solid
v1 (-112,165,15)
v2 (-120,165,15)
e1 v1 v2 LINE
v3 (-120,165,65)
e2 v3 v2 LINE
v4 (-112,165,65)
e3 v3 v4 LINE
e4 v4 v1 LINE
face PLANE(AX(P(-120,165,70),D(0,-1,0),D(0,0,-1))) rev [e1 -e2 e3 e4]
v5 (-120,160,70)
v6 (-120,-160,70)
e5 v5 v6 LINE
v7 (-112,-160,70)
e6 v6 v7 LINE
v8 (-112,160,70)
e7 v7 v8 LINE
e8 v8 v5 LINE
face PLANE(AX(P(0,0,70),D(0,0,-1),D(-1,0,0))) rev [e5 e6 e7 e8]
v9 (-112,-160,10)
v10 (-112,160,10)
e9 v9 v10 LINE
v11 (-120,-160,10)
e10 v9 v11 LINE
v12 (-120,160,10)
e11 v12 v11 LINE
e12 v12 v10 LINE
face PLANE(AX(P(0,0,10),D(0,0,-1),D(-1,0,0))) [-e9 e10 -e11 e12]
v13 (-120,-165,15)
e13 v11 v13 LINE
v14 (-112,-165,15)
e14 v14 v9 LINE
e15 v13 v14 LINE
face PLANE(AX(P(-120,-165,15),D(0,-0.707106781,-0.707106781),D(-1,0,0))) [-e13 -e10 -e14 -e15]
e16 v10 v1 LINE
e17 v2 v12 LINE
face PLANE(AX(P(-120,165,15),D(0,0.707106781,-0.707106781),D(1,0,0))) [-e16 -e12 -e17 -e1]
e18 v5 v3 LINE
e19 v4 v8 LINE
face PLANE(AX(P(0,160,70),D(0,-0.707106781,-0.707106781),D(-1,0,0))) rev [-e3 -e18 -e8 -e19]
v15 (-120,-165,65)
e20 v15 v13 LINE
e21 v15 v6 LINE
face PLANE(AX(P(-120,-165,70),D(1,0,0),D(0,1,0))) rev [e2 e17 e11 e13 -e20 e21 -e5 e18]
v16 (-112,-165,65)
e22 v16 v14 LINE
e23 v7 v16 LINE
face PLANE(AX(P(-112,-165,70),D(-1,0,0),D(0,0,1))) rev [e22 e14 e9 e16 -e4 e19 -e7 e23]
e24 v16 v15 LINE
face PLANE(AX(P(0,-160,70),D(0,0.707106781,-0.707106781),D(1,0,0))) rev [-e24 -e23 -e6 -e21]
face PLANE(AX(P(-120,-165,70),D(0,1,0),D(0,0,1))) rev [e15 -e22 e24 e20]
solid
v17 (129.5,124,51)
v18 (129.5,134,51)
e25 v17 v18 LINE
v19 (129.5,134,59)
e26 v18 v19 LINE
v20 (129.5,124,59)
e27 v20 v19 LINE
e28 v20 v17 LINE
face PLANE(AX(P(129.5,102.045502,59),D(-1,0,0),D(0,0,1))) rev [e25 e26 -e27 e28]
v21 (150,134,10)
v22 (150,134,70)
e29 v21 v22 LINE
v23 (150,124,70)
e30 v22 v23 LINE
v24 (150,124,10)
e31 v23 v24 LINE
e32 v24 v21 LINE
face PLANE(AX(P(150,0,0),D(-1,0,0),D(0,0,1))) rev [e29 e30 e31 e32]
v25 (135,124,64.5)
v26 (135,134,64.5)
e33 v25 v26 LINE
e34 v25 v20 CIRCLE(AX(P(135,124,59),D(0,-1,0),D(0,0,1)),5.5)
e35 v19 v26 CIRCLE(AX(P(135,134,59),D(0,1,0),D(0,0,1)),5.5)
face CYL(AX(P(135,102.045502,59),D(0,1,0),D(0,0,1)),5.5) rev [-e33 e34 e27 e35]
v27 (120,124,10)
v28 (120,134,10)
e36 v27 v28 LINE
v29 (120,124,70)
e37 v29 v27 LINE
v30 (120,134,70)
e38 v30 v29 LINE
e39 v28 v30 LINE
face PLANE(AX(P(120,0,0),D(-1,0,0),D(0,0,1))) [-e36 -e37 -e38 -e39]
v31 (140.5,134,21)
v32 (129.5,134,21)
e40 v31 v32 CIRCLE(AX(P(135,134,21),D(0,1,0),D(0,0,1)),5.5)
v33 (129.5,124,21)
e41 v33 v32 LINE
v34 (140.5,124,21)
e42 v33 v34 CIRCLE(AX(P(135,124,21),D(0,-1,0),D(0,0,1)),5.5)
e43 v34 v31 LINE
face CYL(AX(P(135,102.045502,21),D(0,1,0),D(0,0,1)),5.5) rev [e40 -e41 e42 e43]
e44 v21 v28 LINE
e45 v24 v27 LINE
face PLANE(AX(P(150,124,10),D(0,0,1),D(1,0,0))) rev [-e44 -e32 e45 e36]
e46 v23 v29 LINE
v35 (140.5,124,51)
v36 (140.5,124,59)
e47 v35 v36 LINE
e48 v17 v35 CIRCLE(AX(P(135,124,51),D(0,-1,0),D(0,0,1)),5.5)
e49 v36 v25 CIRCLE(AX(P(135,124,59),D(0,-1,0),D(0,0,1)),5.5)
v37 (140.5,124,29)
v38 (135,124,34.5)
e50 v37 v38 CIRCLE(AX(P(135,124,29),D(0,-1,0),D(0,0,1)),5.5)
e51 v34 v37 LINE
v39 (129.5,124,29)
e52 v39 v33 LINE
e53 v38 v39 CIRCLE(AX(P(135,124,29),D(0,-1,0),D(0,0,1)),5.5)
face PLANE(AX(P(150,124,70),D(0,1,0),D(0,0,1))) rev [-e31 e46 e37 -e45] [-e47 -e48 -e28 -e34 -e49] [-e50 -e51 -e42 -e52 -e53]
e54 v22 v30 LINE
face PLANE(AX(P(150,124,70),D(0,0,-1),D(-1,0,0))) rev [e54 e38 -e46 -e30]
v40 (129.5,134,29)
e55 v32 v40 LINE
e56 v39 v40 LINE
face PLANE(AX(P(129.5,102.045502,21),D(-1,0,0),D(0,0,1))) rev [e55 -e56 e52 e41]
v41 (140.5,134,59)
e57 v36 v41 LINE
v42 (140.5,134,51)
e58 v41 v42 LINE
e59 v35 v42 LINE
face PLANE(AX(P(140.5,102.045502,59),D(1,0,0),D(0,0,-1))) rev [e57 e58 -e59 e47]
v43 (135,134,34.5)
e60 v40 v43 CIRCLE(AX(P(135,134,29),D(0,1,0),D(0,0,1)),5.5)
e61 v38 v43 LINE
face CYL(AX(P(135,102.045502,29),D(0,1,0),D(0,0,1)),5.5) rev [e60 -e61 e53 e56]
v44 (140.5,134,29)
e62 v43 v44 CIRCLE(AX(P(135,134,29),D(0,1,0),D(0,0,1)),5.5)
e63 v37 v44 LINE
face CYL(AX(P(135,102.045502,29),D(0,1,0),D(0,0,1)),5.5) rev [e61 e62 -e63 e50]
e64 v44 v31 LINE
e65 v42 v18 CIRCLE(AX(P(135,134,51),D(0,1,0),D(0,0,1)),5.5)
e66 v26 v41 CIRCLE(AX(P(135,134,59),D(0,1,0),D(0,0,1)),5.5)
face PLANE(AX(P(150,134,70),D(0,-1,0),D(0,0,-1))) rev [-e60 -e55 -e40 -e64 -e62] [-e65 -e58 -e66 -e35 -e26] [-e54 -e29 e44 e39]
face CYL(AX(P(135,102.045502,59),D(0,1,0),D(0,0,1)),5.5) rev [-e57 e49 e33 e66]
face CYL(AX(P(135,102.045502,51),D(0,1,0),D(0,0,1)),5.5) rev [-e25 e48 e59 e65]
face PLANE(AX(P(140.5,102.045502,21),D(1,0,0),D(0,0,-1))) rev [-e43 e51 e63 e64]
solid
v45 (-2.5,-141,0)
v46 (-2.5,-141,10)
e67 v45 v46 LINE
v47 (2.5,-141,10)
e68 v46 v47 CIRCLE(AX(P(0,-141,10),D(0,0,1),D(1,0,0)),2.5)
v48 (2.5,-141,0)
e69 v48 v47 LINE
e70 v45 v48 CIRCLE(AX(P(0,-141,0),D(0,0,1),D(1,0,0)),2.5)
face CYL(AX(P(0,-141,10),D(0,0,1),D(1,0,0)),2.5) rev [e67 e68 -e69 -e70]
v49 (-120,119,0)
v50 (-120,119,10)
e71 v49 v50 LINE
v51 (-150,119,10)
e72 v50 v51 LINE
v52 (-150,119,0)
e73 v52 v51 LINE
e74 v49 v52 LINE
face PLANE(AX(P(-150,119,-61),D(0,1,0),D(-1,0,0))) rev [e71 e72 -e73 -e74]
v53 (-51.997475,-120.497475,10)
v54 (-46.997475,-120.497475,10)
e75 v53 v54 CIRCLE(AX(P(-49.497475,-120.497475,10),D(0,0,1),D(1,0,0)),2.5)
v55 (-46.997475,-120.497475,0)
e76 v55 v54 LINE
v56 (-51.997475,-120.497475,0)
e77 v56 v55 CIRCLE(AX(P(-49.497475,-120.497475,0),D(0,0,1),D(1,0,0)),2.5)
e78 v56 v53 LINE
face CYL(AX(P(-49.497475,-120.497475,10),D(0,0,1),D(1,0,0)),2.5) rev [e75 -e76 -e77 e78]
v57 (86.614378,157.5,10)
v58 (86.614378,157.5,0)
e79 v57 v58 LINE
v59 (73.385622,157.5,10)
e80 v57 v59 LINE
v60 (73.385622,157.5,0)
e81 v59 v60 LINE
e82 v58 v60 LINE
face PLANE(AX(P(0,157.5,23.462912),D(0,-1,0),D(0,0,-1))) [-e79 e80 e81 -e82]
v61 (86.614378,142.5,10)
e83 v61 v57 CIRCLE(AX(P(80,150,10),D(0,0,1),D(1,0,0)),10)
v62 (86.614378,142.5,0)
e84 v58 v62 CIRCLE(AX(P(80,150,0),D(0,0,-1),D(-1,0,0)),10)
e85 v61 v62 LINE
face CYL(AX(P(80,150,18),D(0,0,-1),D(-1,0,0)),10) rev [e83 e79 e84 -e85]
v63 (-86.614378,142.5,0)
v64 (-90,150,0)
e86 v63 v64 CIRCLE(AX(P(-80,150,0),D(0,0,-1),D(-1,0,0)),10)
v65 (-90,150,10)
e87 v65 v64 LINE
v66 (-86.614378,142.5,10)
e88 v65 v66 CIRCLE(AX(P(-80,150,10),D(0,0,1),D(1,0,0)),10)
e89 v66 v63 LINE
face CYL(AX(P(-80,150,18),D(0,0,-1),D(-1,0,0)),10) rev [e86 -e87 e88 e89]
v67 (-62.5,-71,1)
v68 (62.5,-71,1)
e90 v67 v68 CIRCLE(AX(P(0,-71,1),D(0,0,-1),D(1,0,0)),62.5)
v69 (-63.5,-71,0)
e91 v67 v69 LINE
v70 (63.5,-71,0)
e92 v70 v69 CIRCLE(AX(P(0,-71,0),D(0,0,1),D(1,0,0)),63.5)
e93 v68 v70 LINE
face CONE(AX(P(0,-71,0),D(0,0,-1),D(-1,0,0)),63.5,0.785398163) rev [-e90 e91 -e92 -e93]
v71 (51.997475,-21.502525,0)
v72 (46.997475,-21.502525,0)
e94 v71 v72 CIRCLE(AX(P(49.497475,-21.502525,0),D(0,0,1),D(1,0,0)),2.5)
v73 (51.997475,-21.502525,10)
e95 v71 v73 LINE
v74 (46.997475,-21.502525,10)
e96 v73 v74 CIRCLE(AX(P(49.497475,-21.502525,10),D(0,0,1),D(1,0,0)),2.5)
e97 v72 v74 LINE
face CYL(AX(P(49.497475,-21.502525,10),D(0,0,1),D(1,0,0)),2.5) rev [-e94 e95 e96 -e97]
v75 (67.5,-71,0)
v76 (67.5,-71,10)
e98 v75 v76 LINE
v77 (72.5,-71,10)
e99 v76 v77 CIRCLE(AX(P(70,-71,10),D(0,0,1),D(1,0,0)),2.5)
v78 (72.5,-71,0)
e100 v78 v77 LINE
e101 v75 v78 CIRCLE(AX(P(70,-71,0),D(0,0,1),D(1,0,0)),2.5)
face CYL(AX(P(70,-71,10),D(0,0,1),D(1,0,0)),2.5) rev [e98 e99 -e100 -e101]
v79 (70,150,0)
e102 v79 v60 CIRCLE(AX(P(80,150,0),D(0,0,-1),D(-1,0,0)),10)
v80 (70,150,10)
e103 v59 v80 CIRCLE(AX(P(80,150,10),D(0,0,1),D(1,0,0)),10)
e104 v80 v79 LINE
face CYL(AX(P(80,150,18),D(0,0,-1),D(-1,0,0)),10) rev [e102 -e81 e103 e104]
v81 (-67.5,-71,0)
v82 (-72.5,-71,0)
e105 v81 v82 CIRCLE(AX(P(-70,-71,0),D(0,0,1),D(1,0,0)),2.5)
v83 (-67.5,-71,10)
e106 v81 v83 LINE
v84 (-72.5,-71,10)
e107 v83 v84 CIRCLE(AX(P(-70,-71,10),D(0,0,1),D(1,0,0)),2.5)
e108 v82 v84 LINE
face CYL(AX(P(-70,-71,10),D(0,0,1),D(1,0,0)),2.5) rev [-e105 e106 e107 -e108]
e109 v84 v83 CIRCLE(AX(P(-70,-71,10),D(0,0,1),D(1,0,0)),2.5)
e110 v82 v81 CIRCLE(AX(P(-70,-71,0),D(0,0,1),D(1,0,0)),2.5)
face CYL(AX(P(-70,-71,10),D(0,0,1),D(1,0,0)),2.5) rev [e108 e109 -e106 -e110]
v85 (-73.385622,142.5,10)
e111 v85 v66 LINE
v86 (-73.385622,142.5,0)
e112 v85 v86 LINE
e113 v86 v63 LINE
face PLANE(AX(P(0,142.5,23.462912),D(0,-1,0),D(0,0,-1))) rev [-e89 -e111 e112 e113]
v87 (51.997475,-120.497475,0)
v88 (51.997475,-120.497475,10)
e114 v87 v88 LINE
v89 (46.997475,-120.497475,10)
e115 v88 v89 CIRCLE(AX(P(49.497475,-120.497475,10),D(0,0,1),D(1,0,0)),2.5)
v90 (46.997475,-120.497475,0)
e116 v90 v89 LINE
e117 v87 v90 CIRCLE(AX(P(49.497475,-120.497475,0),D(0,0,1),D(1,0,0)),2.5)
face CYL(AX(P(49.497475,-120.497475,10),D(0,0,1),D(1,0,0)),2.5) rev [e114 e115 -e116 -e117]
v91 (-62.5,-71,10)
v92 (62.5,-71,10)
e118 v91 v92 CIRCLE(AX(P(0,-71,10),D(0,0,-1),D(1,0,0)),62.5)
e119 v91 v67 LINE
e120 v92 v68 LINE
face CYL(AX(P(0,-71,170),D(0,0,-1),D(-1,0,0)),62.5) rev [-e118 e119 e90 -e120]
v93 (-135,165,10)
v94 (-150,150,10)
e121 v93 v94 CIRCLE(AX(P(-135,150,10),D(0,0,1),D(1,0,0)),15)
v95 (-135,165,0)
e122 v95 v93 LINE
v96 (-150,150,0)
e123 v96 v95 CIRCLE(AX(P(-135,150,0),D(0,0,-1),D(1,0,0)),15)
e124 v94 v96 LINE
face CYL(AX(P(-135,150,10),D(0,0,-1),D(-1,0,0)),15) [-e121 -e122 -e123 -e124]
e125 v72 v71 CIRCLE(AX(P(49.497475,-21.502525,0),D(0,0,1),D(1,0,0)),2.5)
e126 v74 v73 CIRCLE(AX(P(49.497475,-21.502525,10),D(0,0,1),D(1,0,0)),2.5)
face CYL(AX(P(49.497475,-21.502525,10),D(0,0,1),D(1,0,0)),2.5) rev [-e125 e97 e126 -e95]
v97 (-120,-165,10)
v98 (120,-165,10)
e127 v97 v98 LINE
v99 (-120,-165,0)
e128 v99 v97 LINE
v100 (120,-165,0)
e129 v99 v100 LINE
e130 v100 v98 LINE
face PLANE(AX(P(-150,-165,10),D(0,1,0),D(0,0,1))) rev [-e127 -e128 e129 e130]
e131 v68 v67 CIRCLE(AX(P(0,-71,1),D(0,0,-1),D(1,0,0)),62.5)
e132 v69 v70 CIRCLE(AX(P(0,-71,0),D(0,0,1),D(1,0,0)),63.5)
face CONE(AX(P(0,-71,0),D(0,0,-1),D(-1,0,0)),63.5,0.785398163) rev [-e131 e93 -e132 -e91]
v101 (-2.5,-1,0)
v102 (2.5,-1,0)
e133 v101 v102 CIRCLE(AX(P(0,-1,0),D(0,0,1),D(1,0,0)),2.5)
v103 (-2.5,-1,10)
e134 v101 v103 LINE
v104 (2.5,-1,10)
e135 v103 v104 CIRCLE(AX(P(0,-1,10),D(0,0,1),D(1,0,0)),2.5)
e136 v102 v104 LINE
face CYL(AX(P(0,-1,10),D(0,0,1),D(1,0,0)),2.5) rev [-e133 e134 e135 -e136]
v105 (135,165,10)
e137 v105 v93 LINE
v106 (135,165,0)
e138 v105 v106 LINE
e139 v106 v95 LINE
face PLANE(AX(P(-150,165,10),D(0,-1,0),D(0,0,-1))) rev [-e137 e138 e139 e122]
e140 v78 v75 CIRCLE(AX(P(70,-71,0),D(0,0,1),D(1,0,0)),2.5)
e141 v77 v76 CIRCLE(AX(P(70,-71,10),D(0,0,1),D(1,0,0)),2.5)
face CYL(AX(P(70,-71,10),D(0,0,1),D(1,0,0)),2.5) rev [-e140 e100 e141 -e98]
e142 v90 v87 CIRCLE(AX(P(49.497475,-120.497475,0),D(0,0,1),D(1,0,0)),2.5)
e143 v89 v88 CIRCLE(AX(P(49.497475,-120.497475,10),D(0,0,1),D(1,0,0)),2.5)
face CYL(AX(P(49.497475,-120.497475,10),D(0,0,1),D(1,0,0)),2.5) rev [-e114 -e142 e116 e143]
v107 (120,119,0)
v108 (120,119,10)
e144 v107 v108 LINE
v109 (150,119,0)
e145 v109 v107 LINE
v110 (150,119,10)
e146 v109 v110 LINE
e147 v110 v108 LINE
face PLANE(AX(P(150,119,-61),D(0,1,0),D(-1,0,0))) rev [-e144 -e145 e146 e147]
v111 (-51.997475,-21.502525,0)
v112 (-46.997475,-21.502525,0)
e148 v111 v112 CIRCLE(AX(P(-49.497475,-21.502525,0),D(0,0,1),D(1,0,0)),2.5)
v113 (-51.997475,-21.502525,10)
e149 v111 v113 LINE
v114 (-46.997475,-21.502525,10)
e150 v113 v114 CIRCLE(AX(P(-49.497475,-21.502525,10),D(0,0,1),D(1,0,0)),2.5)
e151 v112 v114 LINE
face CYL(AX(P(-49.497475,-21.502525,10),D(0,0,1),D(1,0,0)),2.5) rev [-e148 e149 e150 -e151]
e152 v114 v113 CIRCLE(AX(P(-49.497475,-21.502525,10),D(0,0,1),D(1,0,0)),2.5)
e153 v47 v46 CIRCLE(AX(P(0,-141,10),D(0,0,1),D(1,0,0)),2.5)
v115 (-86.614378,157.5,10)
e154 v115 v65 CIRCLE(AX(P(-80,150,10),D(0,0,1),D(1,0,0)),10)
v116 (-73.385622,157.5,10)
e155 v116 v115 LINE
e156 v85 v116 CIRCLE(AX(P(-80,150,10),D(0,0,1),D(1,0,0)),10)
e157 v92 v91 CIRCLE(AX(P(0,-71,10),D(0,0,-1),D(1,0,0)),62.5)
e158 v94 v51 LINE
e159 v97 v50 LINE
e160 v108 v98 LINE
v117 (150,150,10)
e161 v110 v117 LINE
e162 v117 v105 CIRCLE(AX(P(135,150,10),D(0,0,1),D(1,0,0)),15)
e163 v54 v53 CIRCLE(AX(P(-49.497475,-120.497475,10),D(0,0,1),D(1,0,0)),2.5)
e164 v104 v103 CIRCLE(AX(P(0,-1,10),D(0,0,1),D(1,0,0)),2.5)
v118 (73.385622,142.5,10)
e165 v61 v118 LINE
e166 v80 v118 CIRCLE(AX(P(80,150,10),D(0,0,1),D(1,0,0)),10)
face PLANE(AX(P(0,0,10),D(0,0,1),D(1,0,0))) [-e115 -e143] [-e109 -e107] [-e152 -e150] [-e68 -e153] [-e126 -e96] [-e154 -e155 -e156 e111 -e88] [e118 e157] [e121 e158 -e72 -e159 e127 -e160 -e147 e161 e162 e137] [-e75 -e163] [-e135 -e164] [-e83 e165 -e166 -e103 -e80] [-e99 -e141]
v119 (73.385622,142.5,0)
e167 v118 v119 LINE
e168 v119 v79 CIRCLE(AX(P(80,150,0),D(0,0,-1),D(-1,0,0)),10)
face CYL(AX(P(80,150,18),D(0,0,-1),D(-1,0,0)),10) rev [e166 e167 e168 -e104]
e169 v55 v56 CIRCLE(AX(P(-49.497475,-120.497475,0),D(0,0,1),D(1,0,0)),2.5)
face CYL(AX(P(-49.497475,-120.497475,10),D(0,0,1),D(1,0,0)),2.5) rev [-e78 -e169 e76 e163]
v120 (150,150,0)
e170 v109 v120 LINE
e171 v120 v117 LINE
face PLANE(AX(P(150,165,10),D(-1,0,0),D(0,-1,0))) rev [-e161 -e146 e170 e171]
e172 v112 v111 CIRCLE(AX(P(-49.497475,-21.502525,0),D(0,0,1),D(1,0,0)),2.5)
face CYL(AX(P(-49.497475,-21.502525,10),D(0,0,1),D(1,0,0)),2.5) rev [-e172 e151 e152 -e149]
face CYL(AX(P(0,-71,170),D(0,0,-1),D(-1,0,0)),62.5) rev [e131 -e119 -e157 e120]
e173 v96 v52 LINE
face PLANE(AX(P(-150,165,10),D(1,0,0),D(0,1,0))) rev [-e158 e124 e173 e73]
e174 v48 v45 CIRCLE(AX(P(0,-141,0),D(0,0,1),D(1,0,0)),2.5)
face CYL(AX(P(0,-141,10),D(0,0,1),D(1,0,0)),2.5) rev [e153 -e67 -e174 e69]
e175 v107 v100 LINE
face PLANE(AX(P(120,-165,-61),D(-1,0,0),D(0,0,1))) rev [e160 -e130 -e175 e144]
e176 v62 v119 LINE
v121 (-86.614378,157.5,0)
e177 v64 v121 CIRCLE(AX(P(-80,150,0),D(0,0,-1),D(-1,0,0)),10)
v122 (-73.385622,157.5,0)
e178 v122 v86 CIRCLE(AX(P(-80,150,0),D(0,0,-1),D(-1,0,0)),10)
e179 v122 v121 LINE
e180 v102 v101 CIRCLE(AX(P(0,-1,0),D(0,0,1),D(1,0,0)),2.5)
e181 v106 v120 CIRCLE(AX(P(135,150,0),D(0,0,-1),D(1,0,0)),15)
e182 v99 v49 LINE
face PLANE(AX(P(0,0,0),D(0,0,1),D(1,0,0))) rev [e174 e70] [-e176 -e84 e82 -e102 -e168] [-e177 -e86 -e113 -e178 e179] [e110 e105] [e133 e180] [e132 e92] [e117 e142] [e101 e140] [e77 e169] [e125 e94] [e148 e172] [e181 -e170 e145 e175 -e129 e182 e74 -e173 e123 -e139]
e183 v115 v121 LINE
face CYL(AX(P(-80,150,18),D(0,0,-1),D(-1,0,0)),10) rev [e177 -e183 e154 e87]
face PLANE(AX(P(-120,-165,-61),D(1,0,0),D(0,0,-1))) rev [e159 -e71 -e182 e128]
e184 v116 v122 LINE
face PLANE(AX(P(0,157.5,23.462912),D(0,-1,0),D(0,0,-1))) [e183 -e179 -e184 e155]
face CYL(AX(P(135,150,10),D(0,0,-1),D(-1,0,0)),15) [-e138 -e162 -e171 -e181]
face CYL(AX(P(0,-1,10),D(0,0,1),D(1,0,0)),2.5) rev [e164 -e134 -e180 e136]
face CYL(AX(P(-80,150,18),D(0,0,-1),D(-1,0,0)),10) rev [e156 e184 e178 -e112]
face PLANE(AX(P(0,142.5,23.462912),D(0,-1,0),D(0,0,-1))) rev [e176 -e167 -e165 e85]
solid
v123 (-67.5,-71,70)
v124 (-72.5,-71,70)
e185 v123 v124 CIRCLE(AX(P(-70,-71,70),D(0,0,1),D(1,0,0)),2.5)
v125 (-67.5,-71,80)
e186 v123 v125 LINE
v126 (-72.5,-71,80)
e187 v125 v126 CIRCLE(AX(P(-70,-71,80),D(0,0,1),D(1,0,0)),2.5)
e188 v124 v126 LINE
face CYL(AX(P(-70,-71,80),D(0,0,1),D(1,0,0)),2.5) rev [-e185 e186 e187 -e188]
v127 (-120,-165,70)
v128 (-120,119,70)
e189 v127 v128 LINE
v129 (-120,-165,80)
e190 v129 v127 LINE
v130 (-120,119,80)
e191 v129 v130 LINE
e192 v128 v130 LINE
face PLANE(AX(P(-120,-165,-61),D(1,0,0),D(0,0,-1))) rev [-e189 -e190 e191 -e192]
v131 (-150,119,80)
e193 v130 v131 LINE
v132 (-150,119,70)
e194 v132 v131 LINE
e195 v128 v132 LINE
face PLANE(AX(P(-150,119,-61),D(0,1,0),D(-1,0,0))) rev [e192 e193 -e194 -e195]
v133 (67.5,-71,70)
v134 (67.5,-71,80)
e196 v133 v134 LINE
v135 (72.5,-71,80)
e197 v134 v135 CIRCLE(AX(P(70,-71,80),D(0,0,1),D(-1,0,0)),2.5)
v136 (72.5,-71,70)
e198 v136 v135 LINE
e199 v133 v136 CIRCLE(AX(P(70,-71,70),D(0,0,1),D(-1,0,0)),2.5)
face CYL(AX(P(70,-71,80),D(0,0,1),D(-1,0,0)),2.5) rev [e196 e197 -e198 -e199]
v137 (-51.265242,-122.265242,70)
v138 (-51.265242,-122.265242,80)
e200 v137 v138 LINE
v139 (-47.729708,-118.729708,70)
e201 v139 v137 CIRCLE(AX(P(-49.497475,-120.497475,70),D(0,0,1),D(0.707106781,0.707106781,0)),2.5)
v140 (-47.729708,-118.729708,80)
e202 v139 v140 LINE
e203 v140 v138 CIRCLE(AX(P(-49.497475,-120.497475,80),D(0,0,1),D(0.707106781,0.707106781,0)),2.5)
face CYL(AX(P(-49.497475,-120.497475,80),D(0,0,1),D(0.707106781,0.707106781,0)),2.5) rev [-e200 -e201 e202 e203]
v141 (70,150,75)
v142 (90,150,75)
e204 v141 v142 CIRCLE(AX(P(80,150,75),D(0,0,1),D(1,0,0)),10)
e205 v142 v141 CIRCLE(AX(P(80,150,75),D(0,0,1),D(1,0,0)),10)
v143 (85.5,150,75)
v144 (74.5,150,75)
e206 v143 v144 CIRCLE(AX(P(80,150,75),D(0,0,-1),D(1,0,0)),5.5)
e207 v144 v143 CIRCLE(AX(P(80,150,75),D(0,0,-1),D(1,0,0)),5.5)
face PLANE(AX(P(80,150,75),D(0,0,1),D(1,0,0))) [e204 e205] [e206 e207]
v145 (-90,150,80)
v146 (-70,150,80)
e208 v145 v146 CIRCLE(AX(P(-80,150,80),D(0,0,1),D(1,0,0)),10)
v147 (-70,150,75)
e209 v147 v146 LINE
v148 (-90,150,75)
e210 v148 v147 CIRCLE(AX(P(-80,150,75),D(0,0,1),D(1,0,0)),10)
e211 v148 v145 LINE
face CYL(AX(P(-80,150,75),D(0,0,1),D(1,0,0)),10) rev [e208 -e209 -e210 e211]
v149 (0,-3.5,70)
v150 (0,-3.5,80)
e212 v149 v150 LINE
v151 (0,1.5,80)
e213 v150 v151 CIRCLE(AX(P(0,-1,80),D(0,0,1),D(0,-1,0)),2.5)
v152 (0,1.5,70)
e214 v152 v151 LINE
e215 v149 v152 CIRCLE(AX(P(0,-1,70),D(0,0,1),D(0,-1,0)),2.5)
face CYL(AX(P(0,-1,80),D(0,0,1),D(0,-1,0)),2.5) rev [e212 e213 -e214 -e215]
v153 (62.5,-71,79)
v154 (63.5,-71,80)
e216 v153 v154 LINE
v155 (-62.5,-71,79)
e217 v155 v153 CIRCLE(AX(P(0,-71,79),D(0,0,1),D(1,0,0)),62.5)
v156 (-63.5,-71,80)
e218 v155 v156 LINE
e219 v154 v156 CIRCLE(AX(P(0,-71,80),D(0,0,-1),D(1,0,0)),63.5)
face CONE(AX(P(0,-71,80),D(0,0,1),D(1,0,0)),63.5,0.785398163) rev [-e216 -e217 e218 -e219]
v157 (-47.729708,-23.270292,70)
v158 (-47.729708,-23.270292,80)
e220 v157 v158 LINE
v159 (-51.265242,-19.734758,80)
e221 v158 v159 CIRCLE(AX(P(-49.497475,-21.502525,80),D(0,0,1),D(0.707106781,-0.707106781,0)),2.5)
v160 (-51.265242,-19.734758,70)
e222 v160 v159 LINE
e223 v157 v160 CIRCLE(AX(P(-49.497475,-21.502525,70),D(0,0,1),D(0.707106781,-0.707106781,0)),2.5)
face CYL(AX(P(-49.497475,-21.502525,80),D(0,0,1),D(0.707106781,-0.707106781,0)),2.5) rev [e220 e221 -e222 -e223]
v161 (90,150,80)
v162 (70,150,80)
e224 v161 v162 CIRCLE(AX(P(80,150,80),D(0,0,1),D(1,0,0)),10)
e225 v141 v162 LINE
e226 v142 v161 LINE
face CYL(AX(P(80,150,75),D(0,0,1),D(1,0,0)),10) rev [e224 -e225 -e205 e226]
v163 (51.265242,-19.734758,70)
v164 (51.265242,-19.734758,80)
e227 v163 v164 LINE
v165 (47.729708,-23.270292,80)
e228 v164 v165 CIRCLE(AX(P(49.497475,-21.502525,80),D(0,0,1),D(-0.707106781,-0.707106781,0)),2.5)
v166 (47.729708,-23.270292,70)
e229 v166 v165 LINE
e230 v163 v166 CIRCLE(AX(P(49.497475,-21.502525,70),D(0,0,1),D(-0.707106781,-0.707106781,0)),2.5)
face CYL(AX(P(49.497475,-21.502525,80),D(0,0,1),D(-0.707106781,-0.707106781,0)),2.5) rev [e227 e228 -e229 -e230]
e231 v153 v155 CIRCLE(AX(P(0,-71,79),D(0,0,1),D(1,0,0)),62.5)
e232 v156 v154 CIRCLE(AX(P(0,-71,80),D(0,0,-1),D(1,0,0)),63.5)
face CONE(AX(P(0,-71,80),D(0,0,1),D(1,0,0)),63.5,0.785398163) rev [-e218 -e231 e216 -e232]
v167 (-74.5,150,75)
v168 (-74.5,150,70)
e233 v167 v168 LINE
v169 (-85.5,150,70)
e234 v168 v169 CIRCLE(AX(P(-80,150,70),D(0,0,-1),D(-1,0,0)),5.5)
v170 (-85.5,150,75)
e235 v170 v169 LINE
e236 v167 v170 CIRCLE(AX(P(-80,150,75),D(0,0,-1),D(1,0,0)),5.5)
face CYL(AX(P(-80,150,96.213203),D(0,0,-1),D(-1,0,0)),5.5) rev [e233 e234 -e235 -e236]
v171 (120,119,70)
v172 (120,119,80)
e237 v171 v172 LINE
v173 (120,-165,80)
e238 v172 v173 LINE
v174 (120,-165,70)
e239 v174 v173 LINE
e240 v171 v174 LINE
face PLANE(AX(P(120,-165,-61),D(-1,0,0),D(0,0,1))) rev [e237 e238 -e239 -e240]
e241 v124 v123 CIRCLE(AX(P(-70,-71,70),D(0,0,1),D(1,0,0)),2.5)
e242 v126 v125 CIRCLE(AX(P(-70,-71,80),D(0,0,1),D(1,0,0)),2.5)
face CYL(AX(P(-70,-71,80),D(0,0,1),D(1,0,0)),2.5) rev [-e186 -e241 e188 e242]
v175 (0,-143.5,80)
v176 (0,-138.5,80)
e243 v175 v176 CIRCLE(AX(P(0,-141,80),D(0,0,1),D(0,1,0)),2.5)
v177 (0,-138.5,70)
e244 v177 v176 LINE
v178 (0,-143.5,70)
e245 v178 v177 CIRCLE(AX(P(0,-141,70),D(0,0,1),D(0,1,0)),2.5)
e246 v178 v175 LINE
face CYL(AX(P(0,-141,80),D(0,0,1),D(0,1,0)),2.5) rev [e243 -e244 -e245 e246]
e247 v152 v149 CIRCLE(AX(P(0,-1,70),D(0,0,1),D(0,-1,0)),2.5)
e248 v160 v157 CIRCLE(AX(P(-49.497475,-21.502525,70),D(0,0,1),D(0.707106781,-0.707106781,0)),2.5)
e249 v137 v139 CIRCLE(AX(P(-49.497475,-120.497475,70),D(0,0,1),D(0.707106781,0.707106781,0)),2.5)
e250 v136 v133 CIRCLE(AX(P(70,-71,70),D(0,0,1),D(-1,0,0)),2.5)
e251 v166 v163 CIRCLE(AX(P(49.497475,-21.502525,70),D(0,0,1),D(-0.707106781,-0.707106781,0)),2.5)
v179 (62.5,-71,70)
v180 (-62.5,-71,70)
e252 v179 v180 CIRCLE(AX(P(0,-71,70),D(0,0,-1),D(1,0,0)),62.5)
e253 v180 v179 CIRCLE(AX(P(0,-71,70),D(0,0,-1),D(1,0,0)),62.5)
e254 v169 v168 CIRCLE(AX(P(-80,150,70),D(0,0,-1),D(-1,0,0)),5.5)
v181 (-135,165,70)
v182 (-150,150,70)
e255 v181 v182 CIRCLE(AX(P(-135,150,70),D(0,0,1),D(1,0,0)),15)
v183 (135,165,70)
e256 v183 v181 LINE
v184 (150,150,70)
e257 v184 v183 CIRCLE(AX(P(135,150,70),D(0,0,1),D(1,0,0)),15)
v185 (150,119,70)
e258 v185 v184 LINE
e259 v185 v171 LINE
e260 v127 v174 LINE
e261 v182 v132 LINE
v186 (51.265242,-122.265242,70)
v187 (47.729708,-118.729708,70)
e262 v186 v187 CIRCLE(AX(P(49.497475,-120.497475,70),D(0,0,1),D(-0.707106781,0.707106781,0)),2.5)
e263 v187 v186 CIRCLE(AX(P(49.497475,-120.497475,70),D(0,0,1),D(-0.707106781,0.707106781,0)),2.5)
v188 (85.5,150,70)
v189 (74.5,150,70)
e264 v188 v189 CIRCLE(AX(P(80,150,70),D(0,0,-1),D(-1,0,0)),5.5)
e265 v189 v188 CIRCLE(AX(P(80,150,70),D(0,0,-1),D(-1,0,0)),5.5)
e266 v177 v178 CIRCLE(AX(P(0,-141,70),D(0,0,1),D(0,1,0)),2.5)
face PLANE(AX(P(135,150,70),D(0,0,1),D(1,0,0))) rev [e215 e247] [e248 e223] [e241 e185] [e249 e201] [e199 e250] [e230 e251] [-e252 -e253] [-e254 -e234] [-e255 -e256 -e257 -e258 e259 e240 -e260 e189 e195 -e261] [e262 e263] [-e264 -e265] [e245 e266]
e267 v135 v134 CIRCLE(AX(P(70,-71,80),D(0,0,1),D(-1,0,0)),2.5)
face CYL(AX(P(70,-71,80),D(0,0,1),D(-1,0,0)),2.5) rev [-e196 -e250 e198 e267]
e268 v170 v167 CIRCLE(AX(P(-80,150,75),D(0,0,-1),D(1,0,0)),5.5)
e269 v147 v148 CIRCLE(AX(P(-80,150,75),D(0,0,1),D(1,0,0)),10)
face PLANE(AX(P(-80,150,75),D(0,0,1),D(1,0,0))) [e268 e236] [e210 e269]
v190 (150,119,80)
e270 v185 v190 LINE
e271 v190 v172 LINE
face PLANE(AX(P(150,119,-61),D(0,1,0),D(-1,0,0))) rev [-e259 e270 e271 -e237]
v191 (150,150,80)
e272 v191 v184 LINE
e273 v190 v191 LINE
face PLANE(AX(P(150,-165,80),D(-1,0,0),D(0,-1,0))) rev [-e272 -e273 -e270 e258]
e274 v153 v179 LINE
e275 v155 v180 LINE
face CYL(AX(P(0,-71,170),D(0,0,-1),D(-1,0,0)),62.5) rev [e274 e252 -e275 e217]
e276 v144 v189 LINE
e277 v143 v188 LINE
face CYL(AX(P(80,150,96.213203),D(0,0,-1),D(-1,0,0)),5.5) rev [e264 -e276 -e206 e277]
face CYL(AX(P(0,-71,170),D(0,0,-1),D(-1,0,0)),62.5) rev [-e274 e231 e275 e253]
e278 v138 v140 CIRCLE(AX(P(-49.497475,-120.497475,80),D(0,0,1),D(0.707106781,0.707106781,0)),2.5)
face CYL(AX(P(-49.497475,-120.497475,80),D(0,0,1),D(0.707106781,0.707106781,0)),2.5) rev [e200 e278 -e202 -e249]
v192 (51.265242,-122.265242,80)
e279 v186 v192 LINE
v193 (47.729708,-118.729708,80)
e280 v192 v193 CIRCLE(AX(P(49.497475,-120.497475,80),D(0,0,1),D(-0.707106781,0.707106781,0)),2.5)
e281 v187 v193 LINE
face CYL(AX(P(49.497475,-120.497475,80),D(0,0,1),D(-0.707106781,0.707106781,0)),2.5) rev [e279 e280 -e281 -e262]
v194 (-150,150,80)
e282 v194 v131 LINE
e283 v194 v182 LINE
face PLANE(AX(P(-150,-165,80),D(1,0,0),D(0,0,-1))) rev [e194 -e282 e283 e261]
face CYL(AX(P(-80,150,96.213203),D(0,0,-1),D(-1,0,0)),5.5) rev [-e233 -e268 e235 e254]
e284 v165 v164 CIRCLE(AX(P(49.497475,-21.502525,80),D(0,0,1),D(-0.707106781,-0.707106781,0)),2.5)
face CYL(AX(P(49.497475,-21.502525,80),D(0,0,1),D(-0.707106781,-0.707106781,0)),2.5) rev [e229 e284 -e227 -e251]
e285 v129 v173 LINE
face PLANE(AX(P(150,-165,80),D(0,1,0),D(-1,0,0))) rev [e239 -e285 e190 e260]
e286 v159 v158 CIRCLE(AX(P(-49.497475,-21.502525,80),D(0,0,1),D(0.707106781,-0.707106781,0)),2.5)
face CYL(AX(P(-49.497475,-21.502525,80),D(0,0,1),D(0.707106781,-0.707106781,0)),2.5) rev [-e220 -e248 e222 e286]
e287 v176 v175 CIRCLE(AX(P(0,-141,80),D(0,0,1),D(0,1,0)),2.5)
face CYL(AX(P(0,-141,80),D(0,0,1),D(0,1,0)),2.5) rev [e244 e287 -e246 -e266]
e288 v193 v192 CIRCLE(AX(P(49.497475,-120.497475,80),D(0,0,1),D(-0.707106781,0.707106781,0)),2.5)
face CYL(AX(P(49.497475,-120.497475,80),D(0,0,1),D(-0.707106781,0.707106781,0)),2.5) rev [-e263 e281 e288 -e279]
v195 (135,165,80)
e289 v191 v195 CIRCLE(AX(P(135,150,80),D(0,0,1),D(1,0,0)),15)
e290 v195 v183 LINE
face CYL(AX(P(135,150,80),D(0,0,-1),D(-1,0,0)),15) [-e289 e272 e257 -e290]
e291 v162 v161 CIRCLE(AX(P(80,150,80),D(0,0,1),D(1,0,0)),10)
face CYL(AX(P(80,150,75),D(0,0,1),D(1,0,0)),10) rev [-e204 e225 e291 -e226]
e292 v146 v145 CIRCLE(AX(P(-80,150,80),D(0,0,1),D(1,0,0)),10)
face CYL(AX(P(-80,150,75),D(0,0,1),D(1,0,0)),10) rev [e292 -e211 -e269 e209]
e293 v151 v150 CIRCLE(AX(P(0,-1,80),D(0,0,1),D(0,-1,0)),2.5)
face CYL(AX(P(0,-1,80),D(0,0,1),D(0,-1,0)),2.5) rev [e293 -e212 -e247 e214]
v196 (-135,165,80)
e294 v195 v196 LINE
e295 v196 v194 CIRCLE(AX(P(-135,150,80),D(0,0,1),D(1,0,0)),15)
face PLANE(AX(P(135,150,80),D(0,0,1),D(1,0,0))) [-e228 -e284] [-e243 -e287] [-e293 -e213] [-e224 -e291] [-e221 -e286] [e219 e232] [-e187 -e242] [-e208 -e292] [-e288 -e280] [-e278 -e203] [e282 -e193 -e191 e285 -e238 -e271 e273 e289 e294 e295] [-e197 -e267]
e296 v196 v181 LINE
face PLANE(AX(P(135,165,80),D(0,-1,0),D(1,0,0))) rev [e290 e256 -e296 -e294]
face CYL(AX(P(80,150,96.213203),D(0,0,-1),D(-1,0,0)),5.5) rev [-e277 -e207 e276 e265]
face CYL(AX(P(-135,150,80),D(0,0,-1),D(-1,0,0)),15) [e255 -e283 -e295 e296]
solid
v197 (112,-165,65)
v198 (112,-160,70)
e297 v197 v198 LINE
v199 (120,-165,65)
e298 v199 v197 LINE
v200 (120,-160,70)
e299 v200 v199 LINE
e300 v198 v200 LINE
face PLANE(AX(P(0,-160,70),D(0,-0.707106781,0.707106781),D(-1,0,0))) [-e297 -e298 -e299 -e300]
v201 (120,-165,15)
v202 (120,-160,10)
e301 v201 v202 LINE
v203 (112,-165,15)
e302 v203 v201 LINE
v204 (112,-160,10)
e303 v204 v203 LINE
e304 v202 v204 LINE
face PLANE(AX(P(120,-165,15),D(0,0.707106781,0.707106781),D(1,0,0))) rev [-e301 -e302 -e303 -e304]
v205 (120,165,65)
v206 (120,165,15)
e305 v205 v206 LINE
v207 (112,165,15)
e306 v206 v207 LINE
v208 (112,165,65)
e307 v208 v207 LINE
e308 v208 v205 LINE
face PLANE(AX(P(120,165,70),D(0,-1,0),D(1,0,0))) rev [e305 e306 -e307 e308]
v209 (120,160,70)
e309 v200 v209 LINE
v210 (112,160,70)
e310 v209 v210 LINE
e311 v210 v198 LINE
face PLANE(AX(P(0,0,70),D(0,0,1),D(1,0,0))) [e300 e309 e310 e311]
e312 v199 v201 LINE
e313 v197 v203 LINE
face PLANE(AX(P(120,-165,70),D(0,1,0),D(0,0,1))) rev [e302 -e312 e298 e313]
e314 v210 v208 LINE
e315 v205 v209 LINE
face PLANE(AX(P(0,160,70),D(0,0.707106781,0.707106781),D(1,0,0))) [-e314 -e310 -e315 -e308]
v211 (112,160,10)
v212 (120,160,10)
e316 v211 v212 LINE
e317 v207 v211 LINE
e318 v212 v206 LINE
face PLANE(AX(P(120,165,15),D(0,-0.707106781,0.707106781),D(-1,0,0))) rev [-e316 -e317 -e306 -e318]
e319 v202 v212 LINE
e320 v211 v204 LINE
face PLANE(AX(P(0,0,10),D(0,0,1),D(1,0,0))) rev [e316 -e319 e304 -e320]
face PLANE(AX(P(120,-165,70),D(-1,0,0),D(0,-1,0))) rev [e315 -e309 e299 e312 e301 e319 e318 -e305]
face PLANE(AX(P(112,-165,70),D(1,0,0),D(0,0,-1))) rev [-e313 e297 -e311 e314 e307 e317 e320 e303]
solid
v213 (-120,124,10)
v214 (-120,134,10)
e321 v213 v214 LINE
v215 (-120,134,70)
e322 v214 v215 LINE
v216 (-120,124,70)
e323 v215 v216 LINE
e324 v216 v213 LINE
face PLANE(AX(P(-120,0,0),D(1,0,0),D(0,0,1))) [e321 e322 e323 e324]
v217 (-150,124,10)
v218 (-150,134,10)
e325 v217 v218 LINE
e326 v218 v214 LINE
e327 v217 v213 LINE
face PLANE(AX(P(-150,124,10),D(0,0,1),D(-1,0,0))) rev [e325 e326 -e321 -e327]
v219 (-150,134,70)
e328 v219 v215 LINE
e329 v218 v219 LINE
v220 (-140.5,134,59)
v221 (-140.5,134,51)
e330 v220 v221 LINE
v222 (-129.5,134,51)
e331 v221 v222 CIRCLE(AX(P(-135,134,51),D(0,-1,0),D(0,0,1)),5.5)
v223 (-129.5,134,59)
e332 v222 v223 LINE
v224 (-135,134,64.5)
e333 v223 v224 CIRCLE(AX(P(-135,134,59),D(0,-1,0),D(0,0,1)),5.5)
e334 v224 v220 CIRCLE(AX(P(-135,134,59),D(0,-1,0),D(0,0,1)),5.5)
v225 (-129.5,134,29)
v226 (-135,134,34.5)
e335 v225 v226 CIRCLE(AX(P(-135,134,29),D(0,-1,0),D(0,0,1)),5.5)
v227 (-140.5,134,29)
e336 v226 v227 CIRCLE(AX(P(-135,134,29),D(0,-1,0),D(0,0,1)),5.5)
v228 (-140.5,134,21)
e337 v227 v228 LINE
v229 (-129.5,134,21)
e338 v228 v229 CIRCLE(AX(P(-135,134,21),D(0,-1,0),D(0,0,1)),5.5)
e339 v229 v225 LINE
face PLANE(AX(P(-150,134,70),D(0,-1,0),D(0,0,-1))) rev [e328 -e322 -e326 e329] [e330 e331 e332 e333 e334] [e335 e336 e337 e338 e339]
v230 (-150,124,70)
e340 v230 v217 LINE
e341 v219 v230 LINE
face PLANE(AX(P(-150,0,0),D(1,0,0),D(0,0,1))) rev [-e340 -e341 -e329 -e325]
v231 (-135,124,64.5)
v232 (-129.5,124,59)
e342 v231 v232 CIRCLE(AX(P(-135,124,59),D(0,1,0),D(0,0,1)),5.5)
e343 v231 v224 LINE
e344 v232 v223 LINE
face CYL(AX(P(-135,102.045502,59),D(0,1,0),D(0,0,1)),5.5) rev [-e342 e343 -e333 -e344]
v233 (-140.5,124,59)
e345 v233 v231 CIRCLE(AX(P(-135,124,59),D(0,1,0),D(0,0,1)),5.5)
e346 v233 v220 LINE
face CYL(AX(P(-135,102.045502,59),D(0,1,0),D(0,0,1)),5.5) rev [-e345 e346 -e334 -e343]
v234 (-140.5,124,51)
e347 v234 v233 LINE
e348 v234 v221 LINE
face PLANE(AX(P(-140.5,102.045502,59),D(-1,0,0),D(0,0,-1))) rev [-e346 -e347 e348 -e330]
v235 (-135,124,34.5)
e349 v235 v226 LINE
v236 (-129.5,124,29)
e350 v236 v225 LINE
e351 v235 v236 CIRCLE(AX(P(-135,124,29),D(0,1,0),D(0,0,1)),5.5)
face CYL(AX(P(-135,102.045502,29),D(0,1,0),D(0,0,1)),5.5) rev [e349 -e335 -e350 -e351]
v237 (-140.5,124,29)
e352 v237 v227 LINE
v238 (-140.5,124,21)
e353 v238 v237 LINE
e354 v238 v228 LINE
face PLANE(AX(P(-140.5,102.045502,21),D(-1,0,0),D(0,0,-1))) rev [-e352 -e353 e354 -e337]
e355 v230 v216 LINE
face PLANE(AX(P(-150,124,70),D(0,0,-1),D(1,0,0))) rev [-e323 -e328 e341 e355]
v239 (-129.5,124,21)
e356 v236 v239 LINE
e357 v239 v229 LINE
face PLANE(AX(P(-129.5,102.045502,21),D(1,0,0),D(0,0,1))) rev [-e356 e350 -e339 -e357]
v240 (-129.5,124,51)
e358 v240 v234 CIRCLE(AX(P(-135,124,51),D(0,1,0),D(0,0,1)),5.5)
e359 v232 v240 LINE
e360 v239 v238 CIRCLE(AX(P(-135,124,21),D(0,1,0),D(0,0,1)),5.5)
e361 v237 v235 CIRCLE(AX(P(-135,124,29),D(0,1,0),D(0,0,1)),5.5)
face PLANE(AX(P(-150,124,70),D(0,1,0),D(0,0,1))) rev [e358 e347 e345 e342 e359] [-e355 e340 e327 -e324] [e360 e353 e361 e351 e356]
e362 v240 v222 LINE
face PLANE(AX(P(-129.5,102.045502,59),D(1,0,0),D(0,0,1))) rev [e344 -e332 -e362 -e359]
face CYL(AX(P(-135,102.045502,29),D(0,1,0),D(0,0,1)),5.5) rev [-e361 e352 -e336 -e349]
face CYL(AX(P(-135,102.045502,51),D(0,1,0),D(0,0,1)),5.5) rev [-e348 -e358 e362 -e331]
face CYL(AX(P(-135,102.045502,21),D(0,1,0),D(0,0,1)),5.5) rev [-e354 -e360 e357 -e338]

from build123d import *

# Parameters (mm, degrees)
SKETCH1_W             = 300
SKETCH1_H             = 330
BOSS_EXTRUDE1_DEPTH   = 10
SKETCH2_R             = 7.5
CUT_EXTRUDE1_DEPTH    = 10
LPATTERN1_COUNT       = 2
LPATTERN1_PITCH       = 160
SKETCH12_W            = 8
SKETCH12_H            = 330
BOSS_EXTRUDE2_DEPTH   = 60
BOSS_EXTRUDE2_2_DEPTH = 60
SKETCH13_R            = 7.5
BOSS_EXTRUDE3_DEPTH   = 10
SKETCH14_W            = 60
SKETCH14_H            = 10
BOSS_EXTRUDE4_DEPTH   = 30
CUT_EXTRUDE6_DEPTH    = 10
FILLET1_R             = 15
SKETCH3_R             = 62.5
CUT_EXTRUDE2_DEPTH    = 170
CIRPATTERN1_COUNT     = 8
SKETCH16_W            = 30
SKETCH16_H            = 284
CUT_EXTRUDE3_DEPTH    = 141
CIRPATTERN2_COUNT     = 8
SKETCH21_R            = 10
CUT_EXTRUDE4_DEPTH    = 18
LPATTERN2_COUNT       = 2
LPATTERN2_PITCH       = 160
CUT_EXTRUDE5_START    = -5
SKETCH22_R            = 10
CUT_EXTRUDE5_DEPTH    = 5
CHAMFER1_SIZE         = 1
CHAMFER2_SIZE         = 1
SKETCH23_R            = 7.5
SKETCH23_R_2          = 5.5
BOSS_EXTRUDE5_DEPTH   = 5
BOSS_EXTRUDE6_DEPTH   = 10
CHAMFER3_SIZE         = 5
CHAMFER4_SIZE         = 5


with BuildPart() as part:
    # Sketch1 → Boss-Extrude1 (new body)
    with BuildSketch(Plane.XY):
        Rectangle(SKETCH1_W, SKETCH1_H)
    extrude(amount=BOSS_EXTRUDE1_DEPTH)

    # Sketch2 → Cut-Extrude1 (cut)
    with BuildSketch(Plane.XY.offset(10)):
        with Locations((-80, 150)):
            Circle(SKETCH2_R)
    cut_extrude1 = extrude(amount=-CUT_EXTRUDE1_DEPTH, mode=Mode.SUBTRACT)

    # LPattern1: Cut-Extrude1 ×2
    with Locations(*[(i * LPATTERN1_PITCH, 0, 0) for i in range(1, LPATTERN1_COUNT)]):
        add(cut_extrude1, mode=Mode.SUBTRACT)

    # Fillet1
    fillet1_edges = [part.edges().sort_by_distance(p)[0] for p in [
        (-150, 165, 5),
        (150, 165, 5),
    ]]
    fillet(fillet1_edges, radius=FILLET1_R)


with BuildPart() as body_2:
    # Sketch12 → Boss-Extrude2 (new body)
    with BuildSketch(Plane.XY.offset(10)):
        with Locations((116, 0)):
            Rectangle(SKETCH12_W, SKETCH12_H)
    extrude(amount=BOSS_EXTRUDE2_DEPTH)

    # Chamfer4
    chamfer4_edges = [body_2.edges().sort_by_distance(p)[0] for p in [
        (116, -165, 70),
        (116, -165, 10),
        (116, 165, 10),
        (116, 165, 70),
    ]]
    chamfer(chamfer4_edges, length=CHAMFER4_SIZE)


with BuildPart() as body_3:
    # Sketch12 → Boss-Extrude2 2 (new body)
    with BuildSketch(Plane.XY.offset(10)):
        with Locations((-116, 0)):
            Rectangle(SKETCH12_W, SKETCH12_H)
    extrude(amount=BOSS_EXTRUDE2_2_DEPTH)

    # Chamfer3
    chamfer3_edges = [body_3.edges().sort_by_distance(p)[0] for p in [
        (-116, 165, 70),
        (-116, 165, 10),
        (-116, -165, 10),
        (-116, -165, 70),
    ]]
    chamfer(chamfer3_edges, length=CHAMFER3_SIZE)


with BuildPart() as body_4:
    # Sketch13 → Boss-Extrude3 (new body)
    with BuildSketch(Plane.XY.offset(70)):
        with BuildLine():
            Line((150, -165), (-150, -165))
            Line((-150, -165), (-150, 150))
            ThreePointArc((-150, 150), (-145.606601718, 160.606601718), (-135, 165))
            Line((-135, 165), (135, 165))
            ThreePointArc((135, 165), (145.606601718, 160.606601718), (150, 150))
            Line((150, 150), (150, -165))
        make_face()
        with Locations((80, 150)):
            Circle(SKETCH13_R, mode=Mode.SUBTRACT)
        with Locations((-80, 150)):
            Circle(SKETCH13_R, mode=Mode.SUBTRACT)
    extrude(amount=BOSS_EXTRUDE3_DEPTH)


with BuildPart() as body_5:
    # Sketch14 → Boss-Extrude4 (new body)
    with BuildSketch(Plane(origin=(120, 0, 0), x_dir=(0, 0, -1), z_dir=(1, 0, 0))):
        with Locations((-40, 129)):
            Rectangle(SKETCH14_W, SKETCH14_H)
    extrude(amount=BOSS_EXTRUDE4_DEPTH)

    # Sketch26 → Cut-Extrude6 (cut)
    with BuildSketch(Plane(origin=(0, 134, 0), x_dir=(1, 0, 0), z_dir=(0, 1, 0))):
        with BuildLine():
            Line((140.5, -21), (140.5, -29))
            ThreePointArc((140.5, -29), (135, -34.5), (129.5, -29))
            Line((129.5, -29), (129.5, -21))
            ThreePointArc((129.5, -21), (135, -15.5), (140.5, -21))
        make_face()
        with BuildLine():
            Line((129.5, -59), (129.5, -51))
            ThreePointArc((129.5, -51), (135, -45.5), (140.5, -51))
            Line((140.5, -51), (140.5, -59))
            ThreePointArc((140.5, -59), (135, -64.5), (129.5, -59))
        make_face()
    extrude(amount=-CUT_EXTRUDE6_DEPTH, mode=Mode.SUBTRACT)


with BuildPart() as body_6:
    # Mirror1: mirrored copy
    add(body_5.part.mirror(Plane(origin=(0, 0, 0), x_dir=(0, 0, 1), z_dir=(1, 0, 0))))


with BuildPart() as cut_extrude2_tool:
    # Sketch3 → Cut-Extrude2 (new body)
    with BuildSketch(Plane.XY):
        with Locations((0, -71)):
            Circle(SKETCH3_R)
    extrude(amount=CUT_EXTRUDE2_DEPTH)


with BuildPart() as part_1:
    add(part.part)

    # Cut-Extrude2: cut by cut_extrude2_tool
    add(cut_extrude2_tool.part, mode=Mode.SUBTRACT)

    # Sketch5 → M6 Tapped Hole1 (revolve, cut)
    with BuildSketch(Plane(origin=(49.497474683, -21.502525317, 10), x_dir=(0, -1, 0), z_dir=(1, 0, 0))):
        Polygon((0, 0), (0, 18.502151548), (2.5, 17), (2.5, 0), align=None)
    m6_tapped_hole1 = revolve(axis=Axis((49.497474683, -21.502525317, 16.35), (0, 0, -1)), mode=Mode.SUBTRACT)

    # CirPattern1: M6 Tapped Hole1 ×8 about axis
    cirpattern1_axis = Axis((0, -71, 0), (0, 0, 1))
    for i in range(1, CIRPATTERN1_COUNT):
        add(m6_tapped_hole1.rotate(cirpattern1_axis, i * 360 / CIRPATTERN1_COUNT), mode=Mode.SUBTRACT)


with BuildPart() as body_4_1:
    add(body_4.part)

    # Cut-Extrude2: cut by cut_extrude2_tool
    add(cut_extrude2_tool.part, mode=Mode.SUBTRACT)


with BuildPart() as cut_extrude3_tool:
    # Sketch16 → Cut-Extrude3 (new body)
    with BuildSketch(Plane.XY.offset(80)):
        with Locations((135, -23)):
            Rectangle(SKETCH16_W, SKETCH16_H)
        with Locations((-135, -23)):
            Rectangle(SKETCH16_W, SKETCH16_H)
    extrude(amount=-CUT_EXTRUDE3_DEPTH)


with BuildPart() as part_2:
    add(part_1.part)

    # Cut-Extrude3: cut by cut_extrude3_tool
    add(cut_extrude3_tool.part, mode=Mode.SUBTRACT)

    # Sketch21 → Cut-Extrude4 (cut)
    with BuildSketch(Plane(origin=(0, 0, 0), x_dir=(-1, 0, 0), z_dir=(0, 0, -1))):
        with Locations((-80, 150)):
            Circle(SKETCH21_R)
    cut_extrude4 = extrude(amount=-CUT_EXTRUDE4_DEPTH, mode=Mode.SUBTRACT)

    # LPattern2: Cut-Extrude4 ×2
    with Locations(*[(-i * LPATTERN2_PITCH, 0, 0) for i in range(1, LPATTERN2_COUNT)]):
        add(cut_extrude4, mode=Mode.SUBTRACT)

    # Chamfer2
    chamfer2_edges = [part_2.edges().sort_by_distance(p)[0] for p in [
        (-62.5, -71, 0),
    ]]
    chamfer(chamfer2_edges, length=CHAMFER2_SIZE)

    # Sketch24 → Boss-Extrude6 (add)
    with BuildSketch(Plane(origin=(0, 0, 0), x_dir=(-1, 0, 0), z_dir=(0, 0, -1))):
        with BuildLine():
            ThreePointArc((86.614378278, 157.5), (80, 160), (73.385621722, 157.5))
            Line((73.385621722, 157.5), (86.614378278, 157.5))
        make_face()
        with BuildLine():
            Line((86.614378278, 142.5), (73.385621722, 142.5))
            ThreePointArc((73.385621722, 142.5), (80, 140), (86.614378278, 142.5))
        make_face()
        with BuildLine():
            ThreePointArc((-73.385621722, 157.5), (-80, 160), (-86.614378278, 157.5))
            Line((-86.614378278, 157.5), (-73.385621722, 157.5))
        make_face()
        with BuildLine():
            Line((-73.385621722, 142.5), (-86.614378278, 142.5))
            ThreePointArc((-86.614378278, 142.5), (-80, 140), (-73.385621722, 142.5))
        make_face()
    extrude(amount=-BOSS_EXTRUDE6_DEPTH)


with BuildPart() as body_4_2:
    add(body_4_1.part)

    # Cut-Extrude3: cut by cut_extrude3_tool
    add(cut_extrude3_tool.part, mode=Mode.SUBTRACT)

    # Sketch20 → M6 Tapped Hole2 (revolve, cut)
    with BuildSketch(Plane(origin=(-70, -71, 80), x_dir=(0, -1, 0), z_dir=(1, 0, 0))):
        Polygon((0, 0), (0, 26.002151548), (2.5, 24.5), (2.5, 0), align=None)
    m6_tapped_hole2 = revolve(axis=Axis((-70, -71, 86.35), (0, 0, -1)), mode=Mode.SUBTRACT)

    # CirPattern2: M6 Tapped Hole2 ×8 about axis
    cirpattern2_axis = Axis((0, -71, 0), (0, 0, 1))
    for i in range(1, CIRPATTERN2_COUNT):
        add(m6_tapped_hole2.rotate(cirpattern2_axis, i * 360 / CIRPATTERN2_COUNT), mode=Mode.SUBTRACT)

    # Sketch22 → Cut-Extrude5 (cut)
    with BuildSketch(Plane.XY.offset(80).offset(CUT_EXTRUDE5_START)):
        with Locations((80, 150)):
            Circle(SKETCH22_R)
        with Locations((-80, 150)):
            Circle(SKETCH22_R)
    extrude(amount=CUT_EXTRUDE5_DEPTH, mode=Mode.SUBTRACT)

    # Chamfer1
    chamfer1_edges = [body_4_2.edges().sort_by_distance(p)[0] for p in [
        (-62.5, -71, 80),
    ]]
    chamfer(chamfer1_edges, length=CHAMFER1_SIZE)

    # Sketch23 → Boss-Extrude5 (add)
    # profile 1 of 2: a face of its own
    with BuildSketch(Plane(origin=(0, 0, 70), x_dir=(-1, 0, 0), z_dir=(0, 0, -1))):
        with Locations((-80, 150)):
            Circle(SKETCH23_R)
        with Locations((-80, 150)):
            Circle(SKETCH23_R_2, mode=Mode.SUBTRACT)
    # profile 2 of 2: a face of its own
    with BuildSketch(Plane(origin=(0, 0, 70), x_dir=(-1, 0, 0), z_dir=(0, 0, -1))):
        with Locations((80, 150)):
            Circle(SKETCH23_R)
        with Locations((80, 150)):
            Circle(SKETCH23_R_2, mode=Mode.SUBTRACT)
    extrude(amount=-BOSS_EXTRUDE5_DEPTH)


solid = Compound([body_2.part, body_3.part, body_5.part, body_6.part, part_2.part, body_4_2.part])
